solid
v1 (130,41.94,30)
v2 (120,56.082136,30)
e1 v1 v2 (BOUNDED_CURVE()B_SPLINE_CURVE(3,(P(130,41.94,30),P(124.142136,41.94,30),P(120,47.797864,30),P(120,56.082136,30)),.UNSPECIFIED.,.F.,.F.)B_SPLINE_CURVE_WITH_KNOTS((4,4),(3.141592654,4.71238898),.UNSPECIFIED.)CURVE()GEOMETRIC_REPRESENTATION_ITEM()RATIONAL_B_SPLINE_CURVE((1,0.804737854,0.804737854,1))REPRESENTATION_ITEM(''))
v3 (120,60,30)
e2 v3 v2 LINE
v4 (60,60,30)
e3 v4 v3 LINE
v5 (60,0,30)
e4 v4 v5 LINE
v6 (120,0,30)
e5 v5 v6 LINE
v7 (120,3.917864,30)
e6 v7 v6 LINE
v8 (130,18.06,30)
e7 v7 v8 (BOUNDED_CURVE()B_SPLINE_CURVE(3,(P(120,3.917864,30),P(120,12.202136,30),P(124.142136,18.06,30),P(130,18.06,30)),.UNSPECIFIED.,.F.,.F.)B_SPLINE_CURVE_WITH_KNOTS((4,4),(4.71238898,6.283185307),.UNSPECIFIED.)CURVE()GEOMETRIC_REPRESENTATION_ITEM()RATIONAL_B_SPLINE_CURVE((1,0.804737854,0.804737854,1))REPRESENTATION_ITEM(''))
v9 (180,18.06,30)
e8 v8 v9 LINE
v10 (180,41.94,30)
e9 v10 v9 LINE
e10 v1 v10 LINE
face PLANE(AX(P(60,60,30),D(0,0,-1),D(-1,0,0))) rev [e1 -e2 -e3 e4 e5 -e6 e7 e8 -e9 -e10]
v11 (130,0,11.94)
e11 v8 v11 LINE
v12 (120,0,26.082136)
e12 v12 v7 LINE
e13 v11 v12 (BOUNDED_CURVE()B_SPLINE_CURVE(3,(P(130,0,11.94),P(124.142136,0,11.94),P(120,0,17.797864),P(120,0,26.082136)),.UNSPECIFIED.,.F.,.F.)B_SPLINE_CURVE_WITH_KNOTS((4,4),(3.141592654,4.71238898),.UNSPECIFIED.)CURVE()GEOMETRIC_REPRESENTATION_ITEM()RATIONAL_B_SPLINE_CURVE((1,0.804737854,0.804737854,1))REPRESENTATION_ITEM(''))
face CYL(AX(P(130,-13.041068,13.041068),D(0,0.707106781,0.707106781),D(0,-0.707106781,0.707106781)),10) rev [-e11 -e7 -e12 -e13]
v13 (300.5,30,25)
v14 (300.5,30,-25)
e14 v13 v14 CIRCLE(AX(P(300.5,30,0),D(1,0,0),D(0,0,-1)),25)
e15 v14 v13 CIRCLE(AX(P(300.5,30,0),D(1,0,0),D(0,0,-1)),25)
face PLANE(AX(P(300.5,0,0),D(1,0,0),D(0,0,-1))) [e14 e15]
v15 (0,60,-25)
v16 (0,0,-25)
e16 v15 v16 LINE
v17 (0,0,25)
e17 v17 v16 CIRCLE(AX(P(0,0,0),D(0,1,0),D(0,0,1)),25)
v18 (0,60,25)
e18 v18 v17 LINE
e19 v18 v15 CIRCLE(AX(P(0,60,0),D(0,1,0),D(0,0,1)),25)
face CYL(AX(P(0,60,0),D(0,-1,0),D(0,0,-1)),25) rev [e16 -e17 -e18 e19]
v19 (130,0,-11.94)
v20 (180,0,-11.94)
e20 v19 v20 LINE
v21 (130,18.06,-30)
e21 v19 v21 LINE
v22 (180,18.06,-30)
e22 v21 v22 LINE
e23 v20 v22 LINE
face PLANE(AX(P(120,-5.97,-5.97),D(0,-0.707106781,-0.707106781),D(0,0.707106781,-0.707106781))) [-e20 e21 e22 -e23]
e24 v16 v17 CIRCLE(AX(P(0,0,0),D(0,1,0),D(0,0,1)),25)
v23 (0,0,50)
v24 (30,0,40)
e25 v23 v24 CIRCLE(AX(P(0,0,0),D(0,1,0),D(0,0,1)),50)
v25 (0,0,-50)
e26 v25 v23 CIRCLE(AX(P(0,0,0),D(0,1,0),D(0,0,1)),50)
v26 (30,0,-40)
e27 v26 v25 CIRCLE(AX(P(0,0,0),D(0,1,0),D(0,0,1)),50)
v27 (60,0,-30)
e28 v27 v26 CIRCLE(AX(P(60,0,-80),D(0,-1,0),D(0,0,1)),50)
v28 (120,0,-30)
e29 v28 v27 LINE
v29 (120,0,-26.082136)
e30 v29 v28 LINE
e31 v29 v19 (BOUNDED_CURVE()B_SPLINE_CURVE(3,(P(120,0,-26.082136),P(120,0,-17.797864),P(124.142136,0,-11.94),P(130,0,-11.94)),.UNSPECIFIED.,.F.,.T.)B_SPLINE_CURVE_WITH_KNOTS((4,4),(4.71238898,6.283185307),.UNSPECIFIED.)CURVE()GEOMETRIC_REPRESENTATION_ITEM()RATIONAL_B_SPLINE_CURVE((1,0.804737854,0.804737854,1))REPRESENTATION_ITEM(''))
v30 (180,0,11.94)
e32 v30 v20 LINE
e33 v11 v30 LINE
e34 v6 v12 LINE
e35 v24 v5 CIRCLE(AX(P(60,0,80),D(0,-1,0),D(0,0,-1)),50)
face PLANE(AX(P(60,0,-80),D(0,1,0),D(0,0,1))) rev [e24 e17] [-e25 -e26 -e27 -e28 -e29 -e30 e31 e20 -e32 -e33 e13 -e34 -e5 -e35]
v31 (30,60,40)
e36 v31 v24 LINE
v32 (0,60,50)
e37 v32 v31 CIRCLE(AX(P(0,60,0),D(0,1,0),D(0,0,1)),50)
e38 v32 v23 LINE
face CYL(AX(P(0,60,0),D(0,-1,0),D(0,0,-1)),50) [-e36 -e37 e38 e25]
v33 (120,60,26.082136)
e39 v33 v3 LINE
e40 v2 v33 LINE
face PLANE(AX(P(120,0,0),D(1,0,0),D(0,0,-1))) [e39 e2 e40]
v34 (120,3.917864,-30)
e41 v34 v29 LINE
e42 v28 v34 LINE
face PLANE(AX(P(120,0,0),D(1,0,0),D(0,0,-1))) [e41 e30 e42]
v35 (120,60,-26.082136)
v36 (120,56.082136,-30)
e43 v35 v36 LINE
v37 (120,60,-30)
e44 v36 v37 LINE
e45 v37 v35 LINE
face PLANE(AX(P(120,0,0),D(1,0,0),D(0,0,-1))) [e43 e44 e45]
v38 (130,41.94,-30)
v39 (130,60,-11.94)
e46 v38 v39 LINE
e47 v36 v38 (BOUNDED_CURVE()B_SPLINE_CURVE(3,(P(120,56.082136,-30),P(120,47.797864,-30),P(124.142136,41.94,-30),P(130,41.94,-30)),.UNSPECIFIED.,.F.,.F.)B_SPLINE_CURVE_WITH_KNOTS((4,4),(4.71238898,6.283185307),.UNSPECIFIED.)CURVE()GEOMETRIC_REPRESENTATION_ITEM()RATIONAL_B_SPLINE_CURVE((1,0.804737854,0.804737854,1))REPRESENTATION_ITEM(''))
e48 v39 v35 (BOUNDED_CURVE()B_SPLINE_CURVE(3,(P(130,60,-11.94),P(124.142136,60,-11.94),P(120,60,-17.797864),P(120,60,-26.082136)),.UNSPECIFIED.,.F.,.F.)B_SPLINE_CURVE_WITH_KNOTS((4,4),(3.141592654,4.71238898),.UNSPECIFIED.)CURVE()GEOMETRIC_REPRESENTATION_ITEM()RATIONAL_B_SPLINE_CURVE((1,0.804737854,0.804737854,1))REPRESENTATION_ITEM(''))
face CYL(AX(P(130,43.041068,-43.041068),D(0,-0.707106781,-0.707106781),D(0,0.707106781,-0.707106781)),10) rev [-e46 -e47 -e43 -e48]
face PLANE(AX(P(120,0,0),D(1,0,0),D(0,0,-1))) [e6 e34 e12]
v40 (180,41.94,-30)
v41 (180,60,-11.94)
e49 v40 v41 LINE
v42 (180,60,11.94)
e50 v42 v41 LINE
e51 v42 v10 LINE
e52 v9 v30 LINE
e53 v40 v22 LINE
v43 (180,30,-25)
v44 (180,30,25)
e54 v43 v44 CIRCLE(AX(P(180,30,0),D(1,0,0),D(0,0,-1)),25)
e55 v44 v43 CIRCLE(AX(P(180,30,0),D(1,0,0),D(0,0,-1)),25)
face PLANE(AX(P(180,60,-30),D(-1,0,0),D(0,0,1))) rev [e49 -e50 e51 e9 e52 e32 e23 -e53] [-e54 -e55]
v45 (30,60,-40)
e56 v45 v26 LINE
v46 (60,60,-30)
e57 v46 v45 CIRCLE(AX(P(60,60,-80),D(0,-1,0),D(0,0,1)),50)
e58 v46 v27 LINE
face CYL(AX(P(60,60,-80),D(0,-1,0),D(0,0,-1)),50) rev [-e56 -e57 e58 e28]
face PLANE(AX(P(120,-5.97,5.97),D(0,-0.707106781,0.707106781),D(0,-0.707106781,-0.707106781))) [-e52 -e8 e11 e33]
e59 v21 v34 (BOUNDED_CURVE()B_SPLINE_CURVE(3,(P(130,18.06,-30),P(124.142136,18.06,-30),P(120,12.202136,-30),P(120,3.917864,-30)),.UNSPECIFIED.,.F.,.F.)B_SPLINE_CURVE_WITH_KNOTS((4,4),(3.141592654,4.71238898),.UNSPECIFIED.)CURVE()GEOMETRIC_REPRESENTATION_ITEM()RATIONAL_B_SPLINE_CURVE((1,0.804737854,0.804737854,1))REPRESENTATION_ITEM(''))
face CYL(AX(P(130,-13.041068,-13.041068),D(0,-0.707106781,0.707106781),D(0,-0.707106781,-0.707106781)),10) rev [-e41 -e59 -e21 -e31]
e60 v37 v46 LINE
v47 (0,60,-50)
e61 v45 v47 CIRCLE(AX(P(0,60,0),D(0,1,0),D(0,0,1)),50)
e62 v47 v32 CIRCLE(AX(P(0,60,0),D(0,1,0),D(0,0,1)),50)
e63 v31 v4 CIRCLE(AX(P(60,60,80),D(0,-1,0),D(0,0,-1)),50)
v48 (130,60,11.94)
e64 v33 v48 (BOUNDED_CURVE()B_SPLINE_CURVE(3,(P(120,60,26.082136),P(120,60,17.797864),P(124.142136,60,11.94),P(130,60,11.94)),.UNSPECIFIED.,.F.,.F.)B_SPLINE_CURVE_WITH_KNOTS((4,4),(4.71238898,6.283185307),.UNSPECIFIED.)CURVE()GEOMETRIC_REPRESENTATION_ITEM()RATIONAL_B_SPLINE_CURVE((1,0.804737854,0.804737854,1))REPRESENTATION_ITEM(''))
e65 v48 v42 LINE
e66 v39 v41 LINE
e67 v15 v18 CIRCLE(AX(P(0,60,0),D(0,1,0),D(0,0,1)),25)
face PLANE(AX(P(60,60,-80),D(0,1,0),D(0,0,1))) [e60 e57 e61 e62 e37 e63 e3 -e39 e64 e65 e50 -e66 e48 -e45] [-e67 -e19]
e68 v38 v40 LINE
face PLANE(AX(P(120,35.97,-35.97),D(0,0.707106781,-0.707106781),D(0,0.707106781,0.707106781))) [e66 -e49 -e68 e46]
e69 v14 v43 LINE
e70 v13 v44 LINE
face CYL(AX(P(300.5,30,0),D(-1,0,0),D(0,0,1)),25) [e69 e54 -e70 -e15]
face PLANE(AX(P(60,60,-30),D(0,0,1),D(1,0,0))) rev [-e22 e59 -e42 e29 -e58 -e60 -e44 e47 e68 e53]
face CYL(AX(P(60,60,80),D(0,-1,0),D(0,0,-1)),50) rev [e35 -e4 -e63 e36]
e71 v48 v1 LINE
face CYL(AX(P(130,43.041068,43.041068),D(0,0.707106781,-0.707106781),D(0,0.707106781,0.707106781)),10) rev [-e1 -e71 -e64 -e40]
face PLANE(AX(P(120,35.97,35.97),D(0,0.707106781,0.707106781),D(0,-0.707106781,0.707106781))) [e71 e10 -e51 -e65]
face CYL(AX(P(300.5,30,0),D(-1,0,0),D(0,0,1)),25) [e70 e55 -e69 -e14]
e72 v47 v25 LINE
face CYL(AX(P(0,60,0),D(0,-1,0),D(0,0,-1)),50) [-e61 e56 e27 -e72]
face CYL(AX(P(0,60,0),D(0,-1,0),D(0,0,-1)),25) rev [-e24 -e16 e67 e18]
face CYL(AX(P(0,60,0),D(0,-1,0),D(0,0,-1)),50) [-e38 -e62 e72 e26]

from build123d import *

# Parameters (mm, degrees)
EYE_PROFILE_SKETCH_R   = 25
EYE_BLOCK_60MM_DEPTH   = 60
NECK_FLATS_CUT_DEPTH   = 60
SKETCH2_4_R            = 25
ROD_BOSS_120_5MM_DEPTH = 120.5
NECK_FILLET_R10_R      = 10


with BuildPart() as part:
    # Eye Profile Sketch → Eye Block 60mm (new body)
    with BuildSketch(Plane(origin=(0, 0, 0), x_dir=(1, 0, 0), z_dir=(0, 1, 0))):
        with BuildLine():
            Line((60, 30), (180, 30))
            Line((180, 30), (180, -30))
            Line((180, -30), (60, -30))
            ThreePointArc((60, -30), (44.188611699, -32.565835097), (30, -40))
            ThreePointArc((30, -40), (-50, 0), (30, 40))
            ThreePointArc((30, 40), (44.188611699, 32.565835097), (60, 30))
        make_face()
        with Locations(Location((0, 0, 0), (0, 0, 270))):
            Circle(EYE_PROFILE_SKETCH_R, mode=Mode.SUBTRACT)
    extrude(amount=EYE_BLOCK_60MM_DEPTH)

    # Neck and Rod Sketch → Neck Flats Cut (cut)
    with BuildSketch(Plane(origin=(180, 0, 0), x_dir=(0, 0, -1), z_dir=(1, 0, 0))):
        Polygon((-11.94, 60), (-30, 60), (-30, 41.94), align=None)
        Polygon((30, 60), (11.94, 60), (30, 41.94), align=None)
        Polygon((-11.94, 0), (-30, 18.06), (-30, 0), align=None)
        Polygon((30, 0), (30, 18.06), (11.94, 0), align=None)
    extrude(amount=-NECK_FLATS_CUT_DEPTH, mode=Mode.SUBTRACT)

    # Sketch2_4 → Rod Boss 120.5mm (add)
    with BuildSketch(Plane(origin=(180, 0, 0), x_dir=(0, 0, -1), z_dir=(1, 0, 0))):
        with Locations((0, 30)):
            Circle(SKETCH2_4_R)
    extrude(amount=ROD_BOSS_120_5MM_DEPTH)

    # Neck Fillet R10
    neck_fillet_r10_edges = [part.edges().sort_by_distance(p)[0] for p in [
        (120, 50.97, -20.97),
        (120, 9.03, 20.97),
        (120, 9.03, -20.97),
        (120, 50.97, 20.97),
    ]]
    fillet(neck_fillet_r10_edges, radius=NECK_FILLET_R10_R)


solid = part.part
